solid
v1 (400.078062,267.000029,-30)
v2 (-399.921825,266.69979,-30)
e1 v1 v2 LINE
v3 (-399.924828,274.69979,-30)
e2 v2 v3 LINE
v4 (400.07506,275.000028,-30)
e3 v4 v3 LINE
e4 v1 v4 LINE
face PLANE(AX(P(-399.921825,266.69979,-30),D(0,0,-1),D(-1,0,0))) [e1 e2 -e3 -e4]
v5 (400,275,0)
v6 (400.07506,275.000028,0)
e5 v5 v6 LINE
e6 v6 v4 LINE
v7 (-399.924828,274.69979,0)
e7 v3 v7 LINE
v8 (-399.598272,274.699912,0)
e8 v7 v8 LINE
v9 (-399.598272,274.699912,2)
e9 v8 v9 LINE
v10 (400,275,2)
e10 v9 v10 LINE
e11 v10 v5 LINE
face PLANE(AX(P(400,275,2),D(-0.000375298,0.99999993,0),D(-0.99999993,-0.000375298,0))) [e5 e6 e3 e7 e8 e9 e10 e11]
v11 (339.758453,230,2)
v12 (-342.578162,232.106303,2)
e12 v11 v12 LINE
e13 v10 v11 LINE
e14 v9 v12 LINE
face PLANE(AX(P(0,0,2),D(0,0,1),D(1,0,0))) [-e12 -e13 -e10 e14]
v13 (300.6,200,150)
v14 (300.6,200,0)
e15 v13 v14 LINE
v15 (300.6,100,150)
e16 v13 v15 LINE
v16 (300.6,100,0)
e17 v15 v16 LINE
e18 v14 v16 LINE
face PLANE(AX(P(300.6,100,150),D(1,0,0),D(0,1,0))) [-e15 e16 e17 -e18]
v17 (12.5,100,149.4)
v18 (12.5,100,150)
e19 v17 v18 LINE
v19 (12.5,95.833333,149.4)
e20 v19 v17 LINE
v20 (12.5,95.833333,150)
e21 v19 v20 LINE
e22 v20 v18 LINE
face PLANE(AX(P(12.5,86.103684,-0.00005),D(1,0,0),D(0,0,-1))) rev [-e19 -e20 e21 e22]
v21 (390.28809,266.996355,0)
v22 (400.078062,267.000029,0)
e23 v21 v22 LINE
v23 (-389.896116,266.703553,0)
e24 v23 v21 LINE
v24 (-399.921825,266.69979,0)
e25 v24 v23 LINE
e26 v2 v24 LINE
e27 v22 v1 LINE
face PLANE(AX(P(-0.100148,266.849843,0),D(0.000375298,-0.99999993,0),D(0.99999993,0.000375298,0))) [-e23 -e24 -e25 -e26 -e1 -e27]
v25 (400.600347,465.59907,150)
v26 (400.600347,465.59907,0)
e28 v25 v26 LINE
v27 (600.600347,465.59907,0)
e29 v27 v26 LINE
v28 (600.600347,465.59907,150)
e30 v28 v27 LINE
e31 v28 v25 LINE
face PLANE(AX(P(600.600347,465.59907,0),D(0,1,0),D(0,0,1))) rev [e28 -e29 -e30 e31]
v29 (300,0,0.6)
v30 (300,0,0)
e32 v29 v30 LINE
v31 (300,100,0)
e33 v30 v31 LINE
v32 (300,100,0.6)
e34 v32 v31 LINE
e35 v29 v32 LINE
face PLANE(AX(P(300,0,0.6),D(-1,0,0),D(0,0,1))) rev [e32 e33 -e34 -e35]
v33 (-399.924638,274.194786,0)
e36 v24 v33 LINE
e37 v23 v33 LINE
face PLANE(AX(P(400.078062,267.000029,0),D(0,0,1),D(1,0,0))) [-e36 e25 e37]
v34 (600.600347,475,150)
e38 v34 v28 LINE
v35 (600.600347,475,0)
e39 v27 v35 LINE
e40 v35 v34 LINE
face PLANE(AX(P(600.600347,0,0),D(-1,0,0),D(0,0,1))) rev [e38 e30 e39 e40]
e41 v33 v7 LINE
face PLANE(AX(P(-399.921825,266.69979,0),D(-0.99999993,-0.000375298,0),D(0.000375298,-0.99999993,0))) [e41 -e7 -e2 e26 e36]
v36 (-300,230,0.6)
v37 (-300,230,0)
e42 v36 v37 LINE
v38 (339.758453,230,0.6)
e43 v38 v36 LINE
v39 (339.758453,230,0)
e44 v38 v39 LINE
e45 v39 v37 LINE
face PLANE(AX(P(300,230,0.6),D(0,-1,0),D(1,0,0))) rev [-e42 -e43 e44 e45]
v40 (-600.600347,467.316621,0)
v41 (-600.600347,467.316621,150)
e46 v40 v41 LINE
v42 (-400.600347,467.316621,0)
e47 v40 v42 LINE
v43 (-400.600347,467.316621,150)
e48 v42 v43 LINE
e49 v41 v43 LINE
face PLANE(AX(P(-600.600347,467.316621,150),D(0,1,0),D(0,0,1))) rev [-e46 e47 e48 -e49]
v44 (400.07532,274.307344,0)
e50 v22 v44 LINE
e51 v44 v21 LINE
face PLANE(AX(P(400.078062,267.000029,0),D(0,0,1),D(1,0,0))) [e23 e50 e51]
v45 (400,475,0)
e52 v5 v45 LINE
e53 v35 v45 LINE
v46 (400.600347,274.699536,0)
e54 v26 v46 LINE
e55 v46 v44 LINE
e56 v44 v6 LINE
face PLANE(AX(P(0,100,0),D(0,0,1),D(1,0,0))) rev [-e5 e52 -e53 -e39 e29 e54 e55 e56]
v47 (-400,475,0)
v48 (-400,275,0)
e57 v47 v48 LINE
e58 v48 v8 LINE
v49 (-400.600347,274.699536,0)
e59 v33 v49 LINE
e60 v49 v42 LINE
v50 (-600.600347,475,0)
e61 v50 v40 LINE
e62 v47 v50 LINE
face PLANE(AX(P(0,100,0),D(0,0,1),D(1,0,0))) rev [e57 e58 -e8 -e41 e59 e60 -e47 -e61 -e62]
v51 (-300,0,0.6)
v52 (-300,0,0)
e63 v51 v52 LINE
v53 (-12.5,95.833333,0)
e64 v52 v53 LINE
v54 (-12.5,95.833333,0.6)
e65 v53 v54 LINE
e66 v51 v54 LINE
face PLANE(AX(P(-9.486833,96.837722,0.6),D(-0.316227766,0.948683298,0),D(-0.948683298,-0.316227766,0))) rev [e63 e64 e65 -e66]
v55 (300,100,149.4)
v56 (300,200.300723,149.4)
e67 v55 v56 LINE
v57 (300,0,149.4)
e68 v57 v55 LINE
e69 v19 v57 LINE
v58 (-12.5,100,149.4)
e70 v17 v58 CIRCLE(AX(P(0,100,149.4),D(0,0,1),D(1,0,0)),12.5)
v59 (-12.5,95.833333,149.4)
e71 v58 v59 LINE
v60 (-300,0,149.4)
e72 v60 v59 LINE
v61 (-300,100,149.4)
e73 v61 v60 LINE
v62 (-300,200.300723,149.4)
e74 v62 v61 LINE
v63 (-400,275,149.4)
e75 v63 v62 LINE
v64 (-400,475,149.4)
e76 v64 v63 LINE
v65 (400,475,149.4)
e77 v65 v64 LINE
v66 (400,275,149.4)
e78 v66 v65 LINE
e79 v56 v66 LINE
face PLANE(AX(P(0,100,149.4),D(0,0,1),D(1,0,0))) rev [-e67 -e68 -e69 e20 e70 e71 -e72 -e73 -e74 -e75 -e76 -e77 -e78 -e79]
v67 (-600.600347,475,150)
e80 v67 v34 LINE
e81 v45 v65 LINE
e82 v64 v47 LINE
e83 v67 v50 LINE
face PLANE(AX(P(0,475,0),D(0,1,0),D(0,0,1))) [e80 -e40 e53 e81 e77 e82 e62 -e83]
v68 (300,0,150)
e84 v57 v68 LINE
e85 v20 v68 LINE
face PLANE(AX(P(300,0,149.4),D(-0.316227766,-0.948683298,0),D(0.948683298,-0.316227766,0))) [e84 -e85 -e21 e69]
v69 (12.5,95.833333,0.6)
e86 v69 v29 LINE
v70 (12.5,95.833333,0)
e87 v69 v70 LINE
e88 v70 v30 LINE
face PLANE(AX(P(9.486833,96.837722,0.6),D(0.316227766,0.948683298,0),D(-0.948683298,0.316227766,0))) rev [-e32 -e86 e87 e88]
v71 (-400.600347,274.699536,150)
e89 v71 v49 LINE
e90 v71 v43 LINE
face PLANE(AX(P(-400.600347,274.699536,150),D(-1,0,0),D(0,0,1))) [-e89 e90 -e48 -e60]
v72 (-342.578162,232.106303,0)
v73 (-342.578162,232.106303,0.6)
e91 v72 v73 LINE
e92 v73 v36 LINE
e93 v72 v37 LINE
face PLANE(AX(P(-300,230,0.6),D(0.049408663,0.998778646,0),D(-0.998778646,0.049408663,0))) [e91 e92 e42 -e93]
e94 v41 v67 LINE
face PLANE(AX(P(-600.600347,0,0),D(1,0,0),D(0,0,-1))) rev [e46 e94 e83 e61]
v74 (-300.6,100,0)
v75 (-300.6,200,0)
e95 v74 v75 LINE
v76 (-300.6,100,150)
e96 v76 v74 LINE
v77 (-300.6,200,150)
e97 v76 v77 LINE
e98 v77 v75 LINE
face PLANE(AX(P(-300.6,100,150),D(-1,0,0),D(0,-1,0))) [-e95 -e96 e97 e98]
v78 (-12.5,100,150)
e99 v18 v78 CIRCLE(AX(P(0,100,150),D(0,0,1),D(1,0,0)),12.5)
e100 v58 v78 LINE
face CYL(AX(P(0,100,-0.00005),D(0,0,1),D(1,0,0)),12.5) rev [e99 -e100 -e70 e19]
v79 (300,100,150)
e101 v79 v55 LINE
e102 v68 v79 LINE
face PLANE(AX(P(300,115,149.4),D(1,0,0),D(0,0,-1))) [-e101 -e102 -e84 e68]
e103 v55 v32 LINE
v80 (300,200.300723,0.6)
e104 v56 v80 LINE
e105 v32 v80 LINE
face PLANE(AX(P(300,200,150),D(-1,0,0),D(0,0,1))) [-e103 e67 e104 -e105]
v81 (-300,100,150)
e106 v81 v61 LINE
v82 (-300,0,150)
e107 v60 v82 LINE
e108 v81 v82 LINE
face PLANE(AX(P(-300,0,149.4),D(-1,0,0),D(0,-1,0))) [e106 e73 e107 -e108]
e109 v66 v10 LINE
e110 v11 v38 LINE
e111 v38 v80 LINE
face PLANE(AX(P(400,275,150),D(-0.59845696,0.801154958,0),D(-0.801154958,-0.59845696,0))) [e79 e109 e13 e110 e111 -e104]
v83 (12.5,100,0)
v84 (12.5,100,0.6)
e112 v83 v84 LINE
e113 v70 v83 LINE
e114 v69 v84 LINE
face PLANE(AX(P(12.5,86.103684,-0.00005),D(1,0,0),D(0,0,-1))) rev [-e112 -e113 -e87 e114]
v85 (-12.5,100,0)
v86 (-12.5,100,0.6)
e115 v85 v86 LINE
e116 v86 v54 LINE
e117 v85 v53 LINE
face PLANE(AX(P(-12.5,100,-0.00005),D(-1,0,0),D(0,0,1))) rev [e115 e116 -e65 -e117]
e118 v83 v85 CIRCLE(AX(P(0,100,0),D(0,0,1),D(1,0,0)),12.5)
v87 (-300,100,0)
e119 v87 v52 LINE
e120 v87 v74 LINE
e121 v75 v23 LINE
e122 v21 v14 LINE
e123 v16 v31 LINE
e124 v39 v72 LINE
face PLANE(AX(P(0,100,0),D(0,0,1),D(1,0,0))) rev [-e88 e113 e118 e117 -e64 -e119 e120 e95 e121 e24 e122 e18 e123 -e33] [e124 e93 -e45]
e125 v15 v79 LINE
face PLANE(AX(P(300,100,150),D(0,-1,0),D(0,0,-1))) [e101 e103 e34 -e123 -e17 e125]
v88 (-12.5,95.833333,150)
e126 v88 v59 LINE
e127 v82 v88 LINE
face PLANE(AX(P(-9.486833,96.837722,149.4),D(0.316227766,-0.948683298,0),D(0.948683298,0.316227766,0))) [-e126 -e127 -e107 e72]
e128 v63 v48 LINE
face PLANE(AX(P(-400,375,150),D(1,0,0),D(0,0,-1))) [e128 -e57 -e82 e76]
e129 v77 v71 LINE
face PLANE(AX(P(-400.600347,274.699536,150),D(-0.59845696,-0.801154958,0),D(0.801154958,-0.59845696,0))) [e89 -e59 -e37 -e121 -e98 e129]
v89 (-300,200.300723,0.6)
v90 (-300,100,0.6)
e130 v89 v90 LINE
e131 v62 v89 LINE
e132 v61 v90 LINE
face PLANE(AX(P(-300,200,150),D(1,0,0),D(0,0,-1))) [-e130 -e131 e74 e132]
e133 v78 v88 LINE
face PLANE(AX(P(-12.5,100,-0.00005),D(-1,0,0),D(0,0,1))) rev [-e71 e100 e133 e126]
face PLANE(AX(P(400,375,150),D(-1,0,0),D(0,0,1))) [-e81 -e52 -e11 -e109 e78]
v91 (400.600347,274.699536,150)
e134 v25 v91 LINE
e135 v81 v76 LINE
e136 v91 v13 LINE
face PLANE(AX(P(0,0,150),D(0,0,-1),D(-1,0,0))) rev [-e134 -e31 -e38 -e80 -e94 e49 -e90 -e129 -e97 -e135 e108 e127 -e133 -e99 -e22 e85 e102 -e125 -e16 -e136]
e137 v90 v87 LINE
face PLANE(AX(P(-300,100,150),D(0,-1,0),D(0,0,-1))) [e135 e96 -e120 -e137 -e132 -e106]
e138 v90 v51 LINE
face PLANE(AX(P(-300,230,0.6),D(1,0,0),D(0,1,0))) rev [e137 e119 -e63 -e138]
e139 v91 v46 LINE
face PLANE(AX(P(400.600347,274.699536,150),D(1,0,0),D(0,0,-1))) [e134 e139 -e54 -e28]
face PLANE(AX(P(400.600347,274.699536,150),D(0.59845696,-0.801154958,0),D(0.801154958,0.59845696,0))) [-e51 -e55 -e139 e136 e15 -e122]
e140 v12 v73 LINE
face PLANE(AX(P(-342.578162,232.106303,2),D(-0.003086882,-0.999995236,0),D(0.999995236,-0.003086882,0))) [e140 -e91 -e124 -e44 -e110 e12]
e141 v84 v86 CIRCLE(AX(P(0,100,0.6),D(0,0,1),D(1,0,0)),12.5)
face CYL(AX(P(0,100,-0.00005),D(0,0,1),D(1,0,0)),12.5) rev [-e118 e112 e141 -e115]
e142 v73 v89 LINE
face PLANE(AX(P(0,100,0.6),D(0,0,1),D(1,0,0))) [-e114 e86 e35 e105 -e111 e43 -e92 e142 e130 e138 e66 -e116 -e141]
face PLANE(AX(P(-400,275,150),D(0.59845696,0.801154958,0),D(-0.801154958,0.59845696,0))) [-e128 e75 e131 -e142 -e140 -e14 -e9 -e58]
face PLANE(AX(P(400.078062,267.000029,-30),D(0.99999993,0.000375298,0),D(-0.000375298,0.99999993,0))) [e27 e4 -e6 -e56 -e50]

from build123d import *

# Parameters (mm, degrees)
EXTRUDE_1_DEPTH     = 0.6
EXTRUDE_2_DEPTH     = 150
EXTRUDE_START       = -0.6
EXTRUDE_3_DEPTH     = 0.6
EXTRUDE_4_DEPTH     = 0.6
CUT_EXTRUDE_1_DEPTH = 569.863461773
EXTRUDE_5_DEPTH     = 100
SKETCH_9_W          = 150
SKETCH_9_H          = 7.683379221
EXTRUDE_6_DEPTH     = 200
SKETCH_11_W         = 150
SKETCH_11_H         = 9.400930001
EXTRUDE_7_DEPTH     = 200
EXTRUDE_10_DEPTH    = 2
SKETCH_16_W         = 799.99994366
SKETCH_16_H         = 30
EXTRUDE_12_DEPTH    = 8


with BuildPart() as part:
    # 草图1 → 凸台-拉伸1 (new body)
    with BuildSketch(Plane.XY):
        with BuildLine():
            Line((300, 0), (300, 230))
            Line((300, 230), (-300, 230))
            Line((-300, 230), (-300, 0))
            Line((-300, 0), (-9.486832981, 96.83772234))
            ThreePointArc((-9.486832981, 96.83772234), (0, 110), (9.486832981, 96.83772234))
            Line((9.486832981, 96.83772234), (300, 0))
        make_face()
    extrude(amount=EXTRUDE_1_DEPTH)

    # 草图4 → 凸台-拉伸2 (add)
    with BuildSketch(Plane(origin=(0, 0, 0), x_dir=(-1, 0, 0), z_dir=(0, 0, -1))):
        Polygon((-400, 375), (-400, 275), (-300, 200.300723127), (-300, 200), (-300, 100), (-300.6, 100), (-300.6, 200), (-400.600347155, 274.699536196), (-400.600347155, 375), align=None)
        Polygon((300, 100), (300.6, 100), (300.6, 200), (400.600347155, 274.699536196), (400.600347155, 375), (400, 375), (400, 275), (300, 200.300723127), (300, 200), align=None)
    extrude(amount=-EXTRUDE_2_DEPTH)

    # 草图5 → 凸台-拉伸3 (add)
    with BuildSketch(Plane.XY.offset(150).offset(EXTRUDE_START)):
        with BuildLine():
            Line((-300, 0), (-300, 100))
            Line((-300, 100), (-300.6, 100))
            Line((-300.6, 100), (-300.6, 200))
            Line((-300.6, 200), (-400.600347155, 274.699536196))
            Line((-400.600347155, 274.699536196), (-400.600347155, 375))
            Line((-400.600347155, 375), (400.600347155, 375))
            Line((400.600347155, 375), (400.600347155, 274.699536196))
            Line((400.600347155, 274.699536196), (300.6, 200))
            Line((300.6, 200), (300.6, 115))
            Line((300.6, 115), (300, 115))
            Line((300, 115), (300, 0))
            Line((300, 0), (9.486832981, 96.83772234))
            ThreePointArc((9.486832981, 96.83772234), (0, 110), (-9.486832981, 96.83772234))
            Line((-9.486832981, 96.83772234), (-300, 0))
        make_face()
    extrude(amount=EXTRUDE_3_DEPTH)

    # 草图6 → 凸台-拉伸4 (add)
    with BuildSketch(Plane(origin=(0, 0, 0), x_dir=(-1, 0, 0), z_dir=(0, 0, -1))):
        with BuildLine():
            Line((-300, 230), (-340.599999933, 230))
            Line((-340.599999933, 230), (-300.6, 200))
            ThreePointArc((-300.6, 200), (-300.207294902, 199.964589803), (-300, 200.3))
            Line((-300, 200.3), (-300, 230))
        make_face()
        Polygon((300, 230), (343.651844708, 232.159416678), (300.6, 200), (300, 200.300723127), align=None)
    extrude(amount=-EXTRUDE_4_DEPTH)

    # 草图7 → 切除-拉伸1 (cut, through all)
    with BuildSketch(Plane.XY.offset(150)):
        with BuildLine():
            Line((-12.5, 100), (-12.5, 86.103683602))
            Line((-12.5, 86.103683602), (12.5, 86.103683602))
            Line((12.5, 86.103683602), (12.5, 100))
            ThreePointArc((12.5, 100), (0, 112.5), (-12.5, 100))
        make_face()
    extrude(amount=-CUT_EXTRUDE_1_DEPTH, mode=Mode.SUBTRACT)

    # 草图8 → 凸台-拉伸5 (add)
    with BuildSketch(Plane(origin=(0, 375, 0), x_dir=(1, 0, 0), z_dir=(0, 1, 0))):
        Polygon((-400.600347155, 0), (-400, 0), (-400, -149.4), (400, -149.4), (400, 0), (400.600347155, 0), (400.600347155, -149.4), (400.600347155, -150), (-400, -150), (-400.600347155, -150), align=None)
    extrude(amount=EXTRUDE_5_DEPTH)

    # 草图9 → 凸台-拉伸6 (add)
    with BuildSketch(Plane.ZY.offset(400.600347155)):
        with Locations((75, 471.15831039)):
            Rectangle(SKETCH_9_W, SKETCH_9_H)
    extrude(amount=EXTRUDE_6_DEPTH)

    # 草图11 → 凸台-拉伸7 (add)
    with BuildSketch(Plane(origin=(400.600347155, 0, 0), x_dir=(0, 0, -1), z_dir=(1, 0, 0))):
        with Locations((-75, 470.299535)):
            Rectangle(SKETCH_11_W, SKETCH_11_H)
    extrude(amount=EXTRUDE_7_DEPTH)

    # 草图12 → 凸台-拉伸10 (add)
    with BuildSketch(Plane(origin=(0, 0, 0), x_dir=(-1, 0, 0), z_dir=(0, 0, -1))):
        Polygon((-339.758452982, 230), (-400, 275), (400.600347155, 274.699536196), (342.578162478, 232.106302604), align=None)
    extrude(amount=-EXTRUDE_10_DEPTH)

    # 草图16 → 凸台-拉伸12 (add)
    with BuildSketch(Plane(origin=(-0.103150629, 274.84984204, 0), x_dir=(0.9999999295756685, 0.00037529809229504854, 0), z_dir=(-0.0003752980922950485, 0.9999999295756684, 0))):
        with Locations((0.178266594, 15)):
            Rectangle(SKETCH_16_W, SKETCH_16_H)
    extrude(amount=-EXTRUDE_12_DEPTH)


solid = part.part
